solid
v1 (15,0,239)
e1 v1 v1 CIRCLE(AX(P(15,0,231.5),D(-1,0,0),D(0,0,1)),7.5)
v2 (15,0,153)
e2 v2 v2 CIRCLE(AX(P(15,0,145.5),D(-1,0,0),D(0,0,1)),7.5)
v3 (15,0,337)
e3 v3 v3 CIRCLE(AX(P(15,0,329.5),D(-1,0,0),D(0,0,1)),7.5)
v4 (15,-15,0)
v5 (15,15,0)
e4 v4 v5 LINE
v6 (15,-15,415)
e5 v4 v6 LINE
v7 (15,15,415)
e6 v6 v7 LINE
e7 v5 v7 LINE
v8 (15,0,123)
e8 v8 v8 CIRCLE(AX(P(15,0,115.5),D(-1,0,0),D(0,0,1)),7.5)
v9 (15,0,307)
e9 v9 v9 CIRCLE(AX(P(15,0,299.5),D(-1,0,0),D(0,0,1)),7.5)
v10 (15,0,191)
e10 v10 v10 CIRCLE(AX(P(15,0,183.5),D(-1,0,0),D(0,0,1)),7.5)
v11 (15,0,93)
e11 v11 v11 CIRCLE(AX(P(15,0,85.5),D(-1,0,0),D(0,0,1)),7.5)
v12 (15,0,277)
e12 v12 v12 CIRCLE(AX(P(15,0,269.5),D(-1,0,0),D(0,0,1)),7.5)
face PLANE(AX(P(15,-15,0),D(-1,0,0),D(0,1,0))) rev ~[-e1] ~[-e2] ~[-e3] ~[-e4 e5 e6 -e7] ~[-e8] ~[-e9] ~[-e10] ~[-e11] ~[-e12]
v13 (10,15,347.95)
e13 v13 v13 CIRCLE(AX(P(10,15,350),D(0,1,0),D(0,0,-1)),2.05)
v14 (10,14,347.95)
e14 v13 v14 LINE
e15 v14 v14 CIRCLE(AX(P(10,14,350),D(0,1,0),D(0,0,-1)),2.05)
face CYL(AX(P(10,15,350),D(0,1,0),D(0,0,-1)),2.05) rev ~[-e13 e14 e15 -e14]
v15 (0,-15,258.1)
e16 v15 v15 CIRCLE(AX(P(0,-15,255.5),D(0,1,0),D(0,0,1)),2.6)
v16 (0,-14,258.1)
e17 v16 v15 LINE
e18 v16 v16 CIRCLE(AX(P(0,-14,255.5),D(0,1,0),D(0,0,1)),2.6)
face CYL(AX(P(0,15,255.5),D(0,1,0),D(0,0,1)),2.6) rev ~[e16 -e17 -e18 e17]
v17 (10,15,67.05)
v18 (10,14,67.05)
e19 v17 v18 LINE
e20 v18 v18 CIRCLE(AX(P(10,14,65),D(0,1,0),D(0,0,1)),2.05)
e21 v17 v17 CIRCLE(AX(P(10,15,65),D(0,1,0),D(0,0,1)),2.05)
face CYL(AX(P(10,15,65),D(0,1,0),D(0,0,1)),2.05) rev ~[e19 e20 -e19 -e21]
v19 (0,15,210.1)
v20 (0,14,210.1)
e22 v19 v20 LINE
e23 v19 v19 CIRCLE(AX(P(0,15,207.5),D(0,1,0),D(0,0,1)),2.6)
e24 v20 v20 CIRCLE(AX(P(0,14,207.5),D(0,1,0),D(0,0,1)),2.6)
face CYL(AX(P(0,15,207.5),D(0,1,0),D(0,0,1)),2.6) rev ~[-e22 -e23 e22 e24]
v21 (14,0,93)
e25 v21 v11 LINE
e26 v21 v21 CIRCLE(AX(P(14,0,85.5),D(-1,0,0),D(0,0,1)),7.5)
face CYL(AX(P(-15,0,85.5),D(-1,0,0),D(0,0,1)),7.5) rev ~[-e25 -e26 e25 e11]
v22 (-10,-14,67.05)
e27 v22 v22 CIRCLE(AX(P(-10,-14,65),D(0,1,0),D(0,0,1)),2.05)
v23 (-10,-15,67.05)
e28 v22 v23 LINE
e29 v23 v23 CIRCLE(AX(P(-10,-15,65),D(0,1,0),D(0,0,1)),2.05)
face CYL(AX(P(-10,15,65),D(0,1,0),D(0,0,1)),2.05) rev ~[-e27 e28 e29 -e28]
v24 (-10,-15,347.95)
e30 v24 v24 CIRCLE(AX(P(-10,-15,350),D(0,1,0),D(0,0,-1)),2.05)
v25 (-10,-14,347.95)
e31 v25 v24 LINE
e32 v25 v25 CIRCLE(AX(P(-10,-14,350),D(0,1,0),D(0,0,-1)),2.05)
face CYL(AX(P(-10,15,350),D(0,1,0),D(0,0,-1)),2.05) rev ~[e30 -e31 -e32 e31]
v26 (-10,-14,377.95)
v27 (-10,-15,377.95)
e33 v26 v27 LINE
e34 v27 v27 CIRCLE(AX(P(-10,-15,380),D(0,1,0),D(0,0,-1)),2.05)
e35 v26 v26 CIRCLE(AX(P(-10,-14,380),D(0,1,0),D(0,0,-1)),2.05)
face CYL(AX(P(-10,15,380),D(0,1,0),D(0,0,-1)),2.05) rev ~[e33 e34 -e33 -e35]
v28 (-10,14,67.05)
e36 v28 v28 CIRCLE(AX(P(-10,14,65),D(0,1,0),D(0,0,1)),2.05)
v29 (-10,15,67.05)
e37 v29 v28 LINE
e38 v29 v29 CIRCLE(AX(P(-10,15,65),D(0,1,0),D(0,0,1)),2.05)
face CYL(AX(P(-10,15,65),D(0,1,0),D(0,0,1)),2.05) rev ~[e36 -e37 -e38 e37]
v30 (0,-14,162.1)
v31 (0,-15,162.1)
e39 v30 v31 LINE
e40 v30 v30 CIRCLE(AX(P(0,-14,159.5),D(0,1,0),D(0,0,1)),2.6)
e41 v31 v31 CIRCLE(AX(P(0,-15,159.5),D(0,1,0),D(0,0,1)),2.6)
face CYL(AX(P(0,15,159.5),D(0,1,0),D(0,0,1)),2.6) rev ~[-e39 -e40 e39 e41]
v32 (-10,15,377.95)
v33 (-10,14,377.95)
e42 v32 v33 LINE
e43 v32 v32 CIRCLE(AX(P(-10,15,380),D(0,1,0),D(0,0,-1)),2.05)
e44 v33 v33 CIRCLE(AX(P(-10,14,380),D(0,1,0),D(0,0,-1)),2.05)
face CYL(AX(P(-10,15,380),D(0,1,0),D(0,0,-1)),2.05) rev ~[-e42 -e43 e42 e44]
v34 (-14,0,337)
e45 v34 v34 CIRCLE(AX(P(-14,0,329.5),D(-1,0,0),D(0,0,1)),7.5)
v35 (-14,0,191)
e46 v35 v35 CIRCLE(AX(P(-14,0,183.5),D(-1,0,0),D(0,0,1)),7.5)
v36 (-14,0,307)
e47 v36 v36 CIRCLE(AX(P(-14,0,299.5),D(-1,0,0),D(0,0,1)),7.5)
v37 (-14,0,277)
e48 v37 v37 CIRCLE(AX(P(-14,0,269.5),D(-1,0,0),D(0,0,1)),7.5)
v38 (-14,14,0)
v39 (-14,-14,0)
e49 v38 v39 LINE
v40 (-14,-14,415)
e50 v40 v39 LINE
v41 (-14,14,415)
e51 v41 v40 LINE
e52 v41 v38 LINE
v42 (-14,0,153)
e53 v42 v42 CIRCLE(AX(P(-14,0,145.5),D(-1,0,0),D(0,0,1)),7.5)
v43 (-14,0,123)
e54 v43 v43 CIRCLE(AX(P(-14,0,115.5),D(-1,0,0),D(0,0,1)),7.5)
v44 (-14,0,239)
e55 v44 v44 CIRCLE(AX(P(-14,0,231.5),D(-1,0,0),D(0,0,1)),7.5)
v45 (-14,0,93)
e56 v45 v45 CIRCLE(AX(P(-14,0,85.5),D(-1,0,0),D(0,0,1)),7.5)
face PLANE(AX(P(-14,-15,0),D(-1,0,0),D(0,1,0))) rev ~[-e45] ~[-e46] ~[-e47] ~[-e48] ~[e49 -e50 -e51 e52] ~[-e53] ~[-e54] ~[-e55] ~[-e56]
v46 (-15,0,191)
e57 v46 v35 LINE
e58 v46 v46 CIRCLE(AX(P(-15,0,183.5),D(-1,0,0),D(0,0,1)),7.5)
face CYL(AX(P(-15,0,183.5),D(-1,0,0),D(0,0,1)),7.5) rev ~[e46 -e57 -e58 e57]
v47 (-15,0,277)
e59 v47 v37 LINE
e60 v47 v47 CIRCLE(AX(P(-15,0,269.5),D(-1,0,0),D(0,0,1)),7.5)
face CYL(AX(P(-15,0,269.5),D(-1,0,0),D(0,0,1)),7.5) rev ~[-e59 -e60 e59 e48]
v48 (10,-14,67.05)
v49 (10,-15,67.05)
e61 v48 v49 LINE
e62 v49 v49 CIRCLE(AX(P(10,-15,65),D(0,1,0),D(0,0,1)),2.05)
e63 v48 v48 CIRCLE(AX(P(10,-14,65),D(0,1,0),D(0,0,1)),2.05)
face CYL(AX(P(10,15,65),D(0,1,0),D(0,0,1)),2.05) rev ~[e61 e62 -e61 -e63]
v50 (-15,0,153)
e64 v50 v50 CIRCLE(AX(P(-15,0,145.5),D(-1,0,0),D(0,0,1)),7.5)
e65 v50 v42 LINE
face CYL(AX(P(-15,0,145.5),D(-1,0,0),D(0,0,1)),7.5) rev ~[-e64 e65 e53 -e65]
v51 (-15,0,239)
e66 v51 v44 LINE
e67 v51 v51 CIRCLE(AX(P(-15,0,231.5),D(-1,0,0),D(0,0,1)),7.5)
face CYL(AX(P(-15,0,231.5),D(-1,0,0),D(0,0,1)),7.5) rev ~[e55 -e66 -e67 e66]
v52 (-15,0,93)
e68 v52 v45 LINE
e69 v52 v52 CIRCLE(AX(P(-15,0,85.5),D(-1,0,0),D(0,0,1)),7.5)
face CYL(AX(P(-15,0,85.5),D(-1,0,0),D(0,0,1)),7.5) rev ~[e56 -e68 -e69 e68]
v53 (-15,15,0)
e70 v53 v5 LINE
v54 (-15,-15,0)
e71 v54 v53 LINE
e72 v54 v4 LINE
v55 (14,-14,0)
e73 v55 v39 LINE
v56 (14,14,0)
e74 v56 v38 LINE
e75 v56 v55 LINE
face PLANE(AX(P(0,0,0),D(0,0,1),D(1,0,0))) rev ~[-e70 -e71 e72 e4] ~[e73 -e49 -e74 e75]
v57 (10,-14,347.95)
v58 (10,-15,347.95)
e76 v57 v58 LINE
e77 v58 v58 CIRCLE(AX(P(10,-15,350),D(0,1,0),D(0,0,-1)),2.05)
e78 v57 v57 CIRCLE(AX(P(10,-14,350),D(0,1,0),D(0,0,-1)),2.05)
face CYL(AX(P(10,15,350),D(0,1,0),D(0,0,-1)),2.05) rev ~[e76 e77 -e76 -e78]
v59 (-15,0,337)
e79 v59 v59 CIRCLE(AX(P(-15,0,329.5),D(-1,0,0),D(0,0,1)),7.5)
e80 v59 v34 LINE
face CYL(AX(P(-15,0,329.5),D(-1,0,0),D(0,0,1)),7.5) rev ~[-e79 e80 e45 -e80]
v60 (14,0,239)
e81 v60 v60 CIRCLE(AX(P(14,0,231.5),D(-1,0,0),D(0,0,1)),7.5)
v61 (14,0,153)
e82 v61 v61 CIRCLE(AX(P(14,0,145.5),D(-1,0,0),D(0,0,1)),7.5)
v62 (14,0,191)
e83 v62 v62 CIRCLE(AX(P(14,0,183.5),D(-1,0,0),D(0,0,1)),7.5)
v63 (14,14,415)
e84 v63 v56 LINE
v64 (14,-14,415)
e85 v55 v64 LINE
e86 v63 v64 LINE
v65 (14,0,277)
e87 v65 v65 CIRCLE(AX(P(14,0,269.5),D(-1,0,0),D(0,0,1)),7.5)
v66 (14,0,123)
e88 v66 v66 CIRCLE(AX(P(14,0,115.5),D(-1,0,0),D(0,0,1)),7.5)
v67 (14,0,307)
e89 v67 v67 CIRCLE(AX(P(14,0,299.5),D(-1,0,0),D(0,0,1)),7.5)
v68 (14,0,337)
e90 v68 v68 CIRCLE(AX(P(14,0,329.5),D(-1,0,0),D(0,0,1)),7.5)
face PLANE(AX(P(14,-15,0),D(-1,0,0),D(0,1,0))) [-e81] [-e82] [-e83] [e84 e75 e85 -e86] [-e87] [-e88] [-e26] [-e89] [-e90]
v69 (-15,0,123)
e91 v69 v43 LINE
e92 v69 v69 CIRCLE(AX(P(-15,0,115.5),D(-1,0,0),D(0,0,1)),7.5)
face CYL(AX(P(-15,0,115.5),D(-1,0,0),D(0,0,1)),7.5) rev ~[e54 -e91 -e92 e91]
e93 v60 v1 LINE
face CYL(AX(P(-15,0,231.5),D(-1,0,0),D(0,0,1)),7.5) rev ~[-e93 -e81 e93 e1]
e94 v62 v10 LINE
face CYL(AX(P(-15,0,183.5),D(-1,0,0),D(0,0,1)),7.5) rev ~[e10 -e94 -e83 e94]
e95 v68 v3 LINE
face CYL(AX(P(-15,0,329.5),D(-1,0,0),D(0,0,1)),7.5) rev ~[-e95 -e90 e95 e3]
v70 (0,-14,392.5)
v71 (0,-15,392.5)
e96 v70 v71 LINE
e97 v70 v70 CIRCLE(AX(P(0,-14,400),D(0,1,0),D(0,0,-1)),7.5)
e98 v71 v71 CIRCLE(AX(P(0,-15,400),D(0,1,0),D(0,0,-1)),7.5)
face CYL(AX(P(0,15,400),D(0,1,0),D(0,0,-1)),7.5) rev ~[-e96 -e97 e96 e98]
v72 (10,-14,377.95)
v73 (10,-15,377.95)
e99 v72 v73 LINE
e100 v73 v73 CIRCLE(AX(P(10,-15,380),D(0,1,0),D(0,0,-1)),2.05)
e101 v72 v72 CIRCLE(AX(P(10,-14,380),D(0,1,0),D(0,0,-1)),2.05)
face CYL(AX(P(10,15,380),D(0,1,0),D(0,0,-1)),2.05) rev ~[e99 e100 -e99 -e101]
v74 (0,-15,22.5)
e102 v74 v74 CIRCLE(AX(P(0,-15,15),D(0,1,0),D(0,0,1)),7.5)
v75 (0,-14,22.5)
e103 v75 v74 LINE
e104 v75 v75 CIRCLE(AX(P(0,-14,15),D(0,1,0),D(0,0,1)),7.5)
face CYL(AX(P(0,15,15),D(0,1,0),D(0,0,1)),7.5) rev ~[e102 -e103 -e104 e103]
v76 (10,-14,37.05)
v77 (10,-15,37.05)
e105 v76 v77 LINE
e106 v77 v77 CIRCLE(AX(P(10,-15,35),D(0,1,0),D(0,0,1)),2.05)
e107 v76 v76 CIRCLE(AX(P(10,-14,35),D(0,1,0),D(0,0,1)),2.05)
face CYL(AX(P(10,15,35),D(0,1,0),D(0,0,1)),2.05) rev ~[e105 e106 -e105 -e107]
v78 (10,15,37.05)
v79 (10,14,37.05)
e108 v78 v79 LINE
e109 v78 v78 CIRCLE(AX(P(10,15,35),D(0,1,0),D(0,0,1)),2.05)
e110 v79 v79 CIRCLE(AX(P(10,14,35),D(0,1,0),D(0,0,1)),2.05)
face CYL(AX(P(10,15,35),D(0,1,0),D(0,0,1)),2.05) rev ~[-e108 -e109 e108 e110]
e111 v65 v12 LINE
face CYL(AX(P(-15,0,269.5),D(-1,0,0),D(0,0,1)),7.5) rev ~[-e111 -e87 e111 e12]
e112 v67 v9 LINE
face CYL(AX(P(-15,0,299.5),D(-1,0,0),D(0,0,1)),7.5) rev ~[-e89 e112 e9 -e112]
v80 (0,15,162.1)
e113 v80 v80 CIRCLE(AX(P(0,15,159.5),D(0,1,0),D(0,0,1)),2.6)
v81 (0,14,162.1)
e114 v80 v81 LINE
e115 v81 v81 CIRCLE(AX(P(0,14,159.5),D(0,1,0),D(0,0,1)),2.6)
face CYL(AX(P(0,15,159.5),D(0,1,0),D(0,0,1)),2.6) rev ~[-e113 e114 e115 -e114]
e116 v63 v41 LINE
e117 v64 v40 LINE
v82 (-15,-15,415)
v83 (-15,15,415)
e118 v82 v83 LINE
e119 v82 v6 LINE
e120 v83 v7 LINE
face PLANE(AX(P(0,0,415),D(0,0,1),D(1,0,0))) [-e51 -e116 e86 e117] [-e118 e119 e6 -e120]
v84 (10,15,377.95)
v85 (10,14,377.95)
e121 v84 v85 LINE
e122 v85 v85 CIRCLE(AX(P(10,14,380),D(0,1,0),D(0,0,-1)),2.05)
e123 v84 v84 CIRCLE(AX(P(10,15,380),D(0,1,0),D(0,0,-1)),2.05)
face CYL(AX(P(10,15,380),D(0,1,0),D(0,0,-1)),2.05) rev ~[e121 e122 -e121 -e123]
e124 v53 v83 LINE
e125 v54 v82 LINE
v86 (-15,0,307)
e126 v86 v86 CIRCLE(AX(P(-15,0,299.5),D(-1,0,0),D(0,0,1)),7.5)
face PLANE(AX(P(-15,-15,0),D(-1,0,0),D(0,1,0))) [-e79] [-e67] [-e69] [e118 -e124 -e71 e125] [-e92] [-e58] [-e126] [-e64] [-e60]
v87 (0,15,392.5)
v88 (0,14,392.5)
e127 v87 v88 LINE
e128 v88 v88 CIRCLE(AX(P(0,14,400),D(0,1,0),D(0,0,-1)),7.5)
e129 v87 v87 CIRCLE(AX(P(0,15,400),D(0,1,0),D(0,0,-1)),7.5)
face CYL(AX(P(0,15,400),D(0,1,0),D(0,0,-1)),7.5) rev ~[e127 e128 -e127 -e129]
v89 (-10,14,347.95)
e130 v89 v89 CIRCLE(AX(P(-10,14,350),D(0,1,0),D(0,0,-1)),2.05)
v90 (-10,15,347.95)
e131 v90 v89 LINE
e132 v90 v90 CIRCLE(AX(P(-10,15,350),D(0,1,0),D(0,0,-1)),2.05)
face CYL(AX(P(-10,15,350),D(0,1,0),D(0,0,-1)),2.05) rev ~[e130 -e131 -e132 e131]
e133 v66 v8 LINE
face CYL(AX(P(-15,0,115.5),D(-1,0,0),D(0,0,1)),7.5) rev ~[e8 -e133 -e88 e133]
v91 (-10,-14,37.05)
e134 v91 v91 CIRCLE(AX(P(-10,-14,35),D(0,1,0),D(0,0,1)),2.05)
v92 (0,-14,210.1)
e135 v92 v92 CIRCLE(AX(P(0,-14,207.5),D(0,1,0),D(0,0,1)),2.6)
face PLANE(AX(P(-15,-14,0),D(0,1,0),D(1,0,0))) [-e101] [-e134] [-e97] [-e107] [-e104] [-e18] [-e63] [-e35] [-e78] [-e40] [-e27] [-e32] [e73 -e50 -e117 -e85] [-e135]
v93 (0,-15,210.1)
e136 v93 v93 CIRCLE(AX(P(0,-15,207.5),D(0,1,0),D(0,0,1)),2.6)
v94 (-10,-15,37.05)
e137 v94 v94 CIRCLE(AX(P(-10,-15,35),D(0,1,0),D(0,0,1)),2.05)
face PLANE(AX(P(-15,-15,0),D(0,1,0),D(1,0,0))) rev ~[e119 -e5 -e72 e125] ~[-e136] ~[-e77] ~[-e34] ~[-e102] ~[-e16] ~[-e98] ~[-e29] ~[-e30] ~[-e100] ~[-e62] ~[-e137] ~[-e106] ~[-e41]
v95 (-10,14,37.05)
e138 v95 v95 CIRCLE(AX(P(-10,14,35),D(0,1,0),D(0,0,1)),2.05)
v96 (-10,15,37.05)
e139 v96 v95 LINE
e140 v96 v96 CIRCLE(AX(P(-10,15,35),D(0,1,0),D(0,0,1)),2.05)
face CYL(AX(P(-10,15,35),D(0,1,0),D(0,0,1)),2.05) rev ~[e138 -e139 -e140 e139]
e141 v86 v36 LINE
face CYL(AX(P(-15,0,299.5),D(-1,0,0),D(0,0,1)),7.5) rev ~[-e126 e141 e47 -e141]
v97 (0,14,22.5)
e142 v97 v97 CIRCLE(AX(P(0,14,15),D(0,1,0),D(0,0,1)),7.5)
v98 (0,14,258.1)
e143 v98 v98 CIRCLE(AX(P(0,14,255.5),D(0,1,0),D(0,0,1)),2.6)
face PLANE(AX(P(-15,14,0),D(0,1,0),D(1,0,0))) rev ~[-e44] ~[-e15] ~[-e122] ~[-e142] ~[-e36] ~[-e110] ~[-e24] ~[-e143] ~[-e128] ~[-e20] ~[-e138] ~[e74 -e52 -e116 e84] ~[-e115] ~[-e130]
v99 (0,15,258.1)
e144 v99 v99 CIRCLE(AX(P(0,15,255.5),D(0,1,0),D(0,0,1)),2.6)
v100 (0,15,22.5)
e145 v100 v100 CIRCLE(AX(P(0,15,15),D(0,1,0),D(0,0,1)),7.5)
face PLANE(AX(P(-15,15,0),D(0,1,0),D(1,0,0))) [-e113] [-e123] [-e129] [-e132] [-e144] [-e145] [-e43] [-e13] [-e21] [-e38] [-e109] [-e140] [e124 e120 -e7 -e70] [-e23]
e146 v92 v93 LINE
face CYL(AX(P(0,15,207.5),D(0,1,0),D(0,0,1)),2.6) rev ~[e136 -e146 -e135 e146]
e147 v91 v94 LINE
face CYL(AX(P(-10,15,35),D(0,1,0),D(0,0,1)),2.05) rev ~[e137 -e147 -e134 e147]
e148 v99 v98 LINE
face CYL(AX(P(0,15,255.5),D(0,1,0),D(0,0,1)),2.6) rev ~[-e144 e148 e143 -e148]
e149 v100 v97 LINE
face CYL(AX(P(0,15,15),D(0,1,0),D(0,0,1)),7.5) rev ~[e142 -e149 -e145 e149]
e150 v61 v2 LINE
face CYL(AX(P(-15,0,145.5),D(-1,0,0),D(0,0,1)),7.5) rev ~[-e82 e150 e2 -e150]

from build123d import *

# Parameters (mm, degrees)
SKETCH_1_W          = 30
SKETCH_1_H          = 30
EXTRUDE_1_DEPTH     = 415
SHELL_1_T           = -1
SKETCH_2_R          = 2.6
SKETCH_2_R_2        = 2.05
CUT_EXTRUDE_1_DEPTH = 417.353215431
SKETCH_3_R          = 7.5
CUT_EXTRUDE_2_DEPTH = 417.353215431
SKETCH_4_R          = 7.5
CUT_EXTRUDE_3_DEPTH = 417.353215431


with BuildPart() as part:
    # 草图1 → 凸台-拉伸1 (new body)
    with BuildSketch(Plane.XY):
        Rectangle(SKETCH_1_W, SKETCH_1_H)
    extrude(amount=EXTRUDE_1_DEPTH)

    # 抽壳1
    shell_1_openings = [part.faces().sort_by_distance(p)[0] for p in [
        (0, 0, 415),
        (0, 0, 0),
    ]]
    offset(amount=SHELL_1_T, openings=shell_1_openings, kind=Kind.INTERSECTION)

    # 草图2 → 切除-拉伸1 (cut, through all)
    with BuildSketch(Plane(origin=(0, 15, 0), x_dir=(1, 0, 0), z_dir=(0, 1, 0))):
        with Locations(Location((0, -159.5, 0), (0, 0, 270))):
            Circle(SKETCH_2_R)
        with Locations(Location((0, -255.5, 0), (0, 0, 270))):
            Circle(SKETCH_2_R)
        with Locations(Location((0, -207.5, 0), (0, 0, 270))):
            Circle(SKETCH_2_R)
        with Locations(Location((-10, -35, 0), (0, 0, 270))):
            Circle(SKETCH_2_R_2)
        with Locations(Location((-10, -380, 0), (0, 0, 90))):
            Circle(SKETCH_2_R_2)
        with Locations(Location((-10, -65, 0), (0, 0, 270))):
            Circle(SKETCH_2_R_2)
        with Locations(Location((-10, -350, 0), (0, 0, 90))):
            Circle(SKETCH_2_R_2)
        with Locations(Location((10, -65, 0), (0, 0, 270))):
            Circle(SKETCH_2_R_2)
        with Locations(Location((10, -350, 0), (0, 0, 90))):
            Circle(SKETCH_2_R_2)
        with Locations(Location((10, -35, 0), (0, 0, 270))):
            Circle(SKETCH_2_R_2)
        with Locations(Location((10, -380, 0), (0, 0, 90))):
            Circle(SKETCH_2_R_2)
    extrude(amount=-CUT_EXTRUDE_1_DEPTH, mode=Mode.SUBTRACT)

    # 草图3 → 切除-拉伸2 (cut, through all)
    with BuildSketch(Plane.ZY.offset(15)):
        with Locations((85.5, 0)):
            Circle(SKETCH_3_R)
        with Locations((115.5, 0)):
            Circle(SKETCH_3_R)
        with Locations((145.5, 0)):
            Circle(SKETCH_3_R)
        with Locations((269.5, 0)):
            Circle(SKETCH_3_R)
        with Locations((299.5, 0)):
            Circle(SKETCH_3_R)
        with Locations((329.5, 0)):
            Circle(SKETCH_3_R)
        with Locations((183.5, 0)):
            Circle(SKETCH_3_R)
        with Locations((231.5, 0)):
            Circle(SKETCH_3_R)
    extrude(amount=-CUT_EXTRUDE_2_DEPTH, mode=Mode.SUBTRACT)

    # 草图4 → 切除-拉伸3 (cut, through all)
    with BuildSketch(Plane(origin=(0, 15, 0), x_dir=(1, 0, 0), z_dir=(0, 1, 0))):
        with Locations(Location((0, -15, 0), (0, 0, 270))):
            Circle(SKETCH_4_R)
        with Locations(Location((0, -400, 0), (0, 0, 90))):
            Circle(SKETCH_4_R)
    extrude(amount=-CUT_EXTRUDE_3_DEPTH, mode=Mode.SUBTRACT)


solid = part.part
